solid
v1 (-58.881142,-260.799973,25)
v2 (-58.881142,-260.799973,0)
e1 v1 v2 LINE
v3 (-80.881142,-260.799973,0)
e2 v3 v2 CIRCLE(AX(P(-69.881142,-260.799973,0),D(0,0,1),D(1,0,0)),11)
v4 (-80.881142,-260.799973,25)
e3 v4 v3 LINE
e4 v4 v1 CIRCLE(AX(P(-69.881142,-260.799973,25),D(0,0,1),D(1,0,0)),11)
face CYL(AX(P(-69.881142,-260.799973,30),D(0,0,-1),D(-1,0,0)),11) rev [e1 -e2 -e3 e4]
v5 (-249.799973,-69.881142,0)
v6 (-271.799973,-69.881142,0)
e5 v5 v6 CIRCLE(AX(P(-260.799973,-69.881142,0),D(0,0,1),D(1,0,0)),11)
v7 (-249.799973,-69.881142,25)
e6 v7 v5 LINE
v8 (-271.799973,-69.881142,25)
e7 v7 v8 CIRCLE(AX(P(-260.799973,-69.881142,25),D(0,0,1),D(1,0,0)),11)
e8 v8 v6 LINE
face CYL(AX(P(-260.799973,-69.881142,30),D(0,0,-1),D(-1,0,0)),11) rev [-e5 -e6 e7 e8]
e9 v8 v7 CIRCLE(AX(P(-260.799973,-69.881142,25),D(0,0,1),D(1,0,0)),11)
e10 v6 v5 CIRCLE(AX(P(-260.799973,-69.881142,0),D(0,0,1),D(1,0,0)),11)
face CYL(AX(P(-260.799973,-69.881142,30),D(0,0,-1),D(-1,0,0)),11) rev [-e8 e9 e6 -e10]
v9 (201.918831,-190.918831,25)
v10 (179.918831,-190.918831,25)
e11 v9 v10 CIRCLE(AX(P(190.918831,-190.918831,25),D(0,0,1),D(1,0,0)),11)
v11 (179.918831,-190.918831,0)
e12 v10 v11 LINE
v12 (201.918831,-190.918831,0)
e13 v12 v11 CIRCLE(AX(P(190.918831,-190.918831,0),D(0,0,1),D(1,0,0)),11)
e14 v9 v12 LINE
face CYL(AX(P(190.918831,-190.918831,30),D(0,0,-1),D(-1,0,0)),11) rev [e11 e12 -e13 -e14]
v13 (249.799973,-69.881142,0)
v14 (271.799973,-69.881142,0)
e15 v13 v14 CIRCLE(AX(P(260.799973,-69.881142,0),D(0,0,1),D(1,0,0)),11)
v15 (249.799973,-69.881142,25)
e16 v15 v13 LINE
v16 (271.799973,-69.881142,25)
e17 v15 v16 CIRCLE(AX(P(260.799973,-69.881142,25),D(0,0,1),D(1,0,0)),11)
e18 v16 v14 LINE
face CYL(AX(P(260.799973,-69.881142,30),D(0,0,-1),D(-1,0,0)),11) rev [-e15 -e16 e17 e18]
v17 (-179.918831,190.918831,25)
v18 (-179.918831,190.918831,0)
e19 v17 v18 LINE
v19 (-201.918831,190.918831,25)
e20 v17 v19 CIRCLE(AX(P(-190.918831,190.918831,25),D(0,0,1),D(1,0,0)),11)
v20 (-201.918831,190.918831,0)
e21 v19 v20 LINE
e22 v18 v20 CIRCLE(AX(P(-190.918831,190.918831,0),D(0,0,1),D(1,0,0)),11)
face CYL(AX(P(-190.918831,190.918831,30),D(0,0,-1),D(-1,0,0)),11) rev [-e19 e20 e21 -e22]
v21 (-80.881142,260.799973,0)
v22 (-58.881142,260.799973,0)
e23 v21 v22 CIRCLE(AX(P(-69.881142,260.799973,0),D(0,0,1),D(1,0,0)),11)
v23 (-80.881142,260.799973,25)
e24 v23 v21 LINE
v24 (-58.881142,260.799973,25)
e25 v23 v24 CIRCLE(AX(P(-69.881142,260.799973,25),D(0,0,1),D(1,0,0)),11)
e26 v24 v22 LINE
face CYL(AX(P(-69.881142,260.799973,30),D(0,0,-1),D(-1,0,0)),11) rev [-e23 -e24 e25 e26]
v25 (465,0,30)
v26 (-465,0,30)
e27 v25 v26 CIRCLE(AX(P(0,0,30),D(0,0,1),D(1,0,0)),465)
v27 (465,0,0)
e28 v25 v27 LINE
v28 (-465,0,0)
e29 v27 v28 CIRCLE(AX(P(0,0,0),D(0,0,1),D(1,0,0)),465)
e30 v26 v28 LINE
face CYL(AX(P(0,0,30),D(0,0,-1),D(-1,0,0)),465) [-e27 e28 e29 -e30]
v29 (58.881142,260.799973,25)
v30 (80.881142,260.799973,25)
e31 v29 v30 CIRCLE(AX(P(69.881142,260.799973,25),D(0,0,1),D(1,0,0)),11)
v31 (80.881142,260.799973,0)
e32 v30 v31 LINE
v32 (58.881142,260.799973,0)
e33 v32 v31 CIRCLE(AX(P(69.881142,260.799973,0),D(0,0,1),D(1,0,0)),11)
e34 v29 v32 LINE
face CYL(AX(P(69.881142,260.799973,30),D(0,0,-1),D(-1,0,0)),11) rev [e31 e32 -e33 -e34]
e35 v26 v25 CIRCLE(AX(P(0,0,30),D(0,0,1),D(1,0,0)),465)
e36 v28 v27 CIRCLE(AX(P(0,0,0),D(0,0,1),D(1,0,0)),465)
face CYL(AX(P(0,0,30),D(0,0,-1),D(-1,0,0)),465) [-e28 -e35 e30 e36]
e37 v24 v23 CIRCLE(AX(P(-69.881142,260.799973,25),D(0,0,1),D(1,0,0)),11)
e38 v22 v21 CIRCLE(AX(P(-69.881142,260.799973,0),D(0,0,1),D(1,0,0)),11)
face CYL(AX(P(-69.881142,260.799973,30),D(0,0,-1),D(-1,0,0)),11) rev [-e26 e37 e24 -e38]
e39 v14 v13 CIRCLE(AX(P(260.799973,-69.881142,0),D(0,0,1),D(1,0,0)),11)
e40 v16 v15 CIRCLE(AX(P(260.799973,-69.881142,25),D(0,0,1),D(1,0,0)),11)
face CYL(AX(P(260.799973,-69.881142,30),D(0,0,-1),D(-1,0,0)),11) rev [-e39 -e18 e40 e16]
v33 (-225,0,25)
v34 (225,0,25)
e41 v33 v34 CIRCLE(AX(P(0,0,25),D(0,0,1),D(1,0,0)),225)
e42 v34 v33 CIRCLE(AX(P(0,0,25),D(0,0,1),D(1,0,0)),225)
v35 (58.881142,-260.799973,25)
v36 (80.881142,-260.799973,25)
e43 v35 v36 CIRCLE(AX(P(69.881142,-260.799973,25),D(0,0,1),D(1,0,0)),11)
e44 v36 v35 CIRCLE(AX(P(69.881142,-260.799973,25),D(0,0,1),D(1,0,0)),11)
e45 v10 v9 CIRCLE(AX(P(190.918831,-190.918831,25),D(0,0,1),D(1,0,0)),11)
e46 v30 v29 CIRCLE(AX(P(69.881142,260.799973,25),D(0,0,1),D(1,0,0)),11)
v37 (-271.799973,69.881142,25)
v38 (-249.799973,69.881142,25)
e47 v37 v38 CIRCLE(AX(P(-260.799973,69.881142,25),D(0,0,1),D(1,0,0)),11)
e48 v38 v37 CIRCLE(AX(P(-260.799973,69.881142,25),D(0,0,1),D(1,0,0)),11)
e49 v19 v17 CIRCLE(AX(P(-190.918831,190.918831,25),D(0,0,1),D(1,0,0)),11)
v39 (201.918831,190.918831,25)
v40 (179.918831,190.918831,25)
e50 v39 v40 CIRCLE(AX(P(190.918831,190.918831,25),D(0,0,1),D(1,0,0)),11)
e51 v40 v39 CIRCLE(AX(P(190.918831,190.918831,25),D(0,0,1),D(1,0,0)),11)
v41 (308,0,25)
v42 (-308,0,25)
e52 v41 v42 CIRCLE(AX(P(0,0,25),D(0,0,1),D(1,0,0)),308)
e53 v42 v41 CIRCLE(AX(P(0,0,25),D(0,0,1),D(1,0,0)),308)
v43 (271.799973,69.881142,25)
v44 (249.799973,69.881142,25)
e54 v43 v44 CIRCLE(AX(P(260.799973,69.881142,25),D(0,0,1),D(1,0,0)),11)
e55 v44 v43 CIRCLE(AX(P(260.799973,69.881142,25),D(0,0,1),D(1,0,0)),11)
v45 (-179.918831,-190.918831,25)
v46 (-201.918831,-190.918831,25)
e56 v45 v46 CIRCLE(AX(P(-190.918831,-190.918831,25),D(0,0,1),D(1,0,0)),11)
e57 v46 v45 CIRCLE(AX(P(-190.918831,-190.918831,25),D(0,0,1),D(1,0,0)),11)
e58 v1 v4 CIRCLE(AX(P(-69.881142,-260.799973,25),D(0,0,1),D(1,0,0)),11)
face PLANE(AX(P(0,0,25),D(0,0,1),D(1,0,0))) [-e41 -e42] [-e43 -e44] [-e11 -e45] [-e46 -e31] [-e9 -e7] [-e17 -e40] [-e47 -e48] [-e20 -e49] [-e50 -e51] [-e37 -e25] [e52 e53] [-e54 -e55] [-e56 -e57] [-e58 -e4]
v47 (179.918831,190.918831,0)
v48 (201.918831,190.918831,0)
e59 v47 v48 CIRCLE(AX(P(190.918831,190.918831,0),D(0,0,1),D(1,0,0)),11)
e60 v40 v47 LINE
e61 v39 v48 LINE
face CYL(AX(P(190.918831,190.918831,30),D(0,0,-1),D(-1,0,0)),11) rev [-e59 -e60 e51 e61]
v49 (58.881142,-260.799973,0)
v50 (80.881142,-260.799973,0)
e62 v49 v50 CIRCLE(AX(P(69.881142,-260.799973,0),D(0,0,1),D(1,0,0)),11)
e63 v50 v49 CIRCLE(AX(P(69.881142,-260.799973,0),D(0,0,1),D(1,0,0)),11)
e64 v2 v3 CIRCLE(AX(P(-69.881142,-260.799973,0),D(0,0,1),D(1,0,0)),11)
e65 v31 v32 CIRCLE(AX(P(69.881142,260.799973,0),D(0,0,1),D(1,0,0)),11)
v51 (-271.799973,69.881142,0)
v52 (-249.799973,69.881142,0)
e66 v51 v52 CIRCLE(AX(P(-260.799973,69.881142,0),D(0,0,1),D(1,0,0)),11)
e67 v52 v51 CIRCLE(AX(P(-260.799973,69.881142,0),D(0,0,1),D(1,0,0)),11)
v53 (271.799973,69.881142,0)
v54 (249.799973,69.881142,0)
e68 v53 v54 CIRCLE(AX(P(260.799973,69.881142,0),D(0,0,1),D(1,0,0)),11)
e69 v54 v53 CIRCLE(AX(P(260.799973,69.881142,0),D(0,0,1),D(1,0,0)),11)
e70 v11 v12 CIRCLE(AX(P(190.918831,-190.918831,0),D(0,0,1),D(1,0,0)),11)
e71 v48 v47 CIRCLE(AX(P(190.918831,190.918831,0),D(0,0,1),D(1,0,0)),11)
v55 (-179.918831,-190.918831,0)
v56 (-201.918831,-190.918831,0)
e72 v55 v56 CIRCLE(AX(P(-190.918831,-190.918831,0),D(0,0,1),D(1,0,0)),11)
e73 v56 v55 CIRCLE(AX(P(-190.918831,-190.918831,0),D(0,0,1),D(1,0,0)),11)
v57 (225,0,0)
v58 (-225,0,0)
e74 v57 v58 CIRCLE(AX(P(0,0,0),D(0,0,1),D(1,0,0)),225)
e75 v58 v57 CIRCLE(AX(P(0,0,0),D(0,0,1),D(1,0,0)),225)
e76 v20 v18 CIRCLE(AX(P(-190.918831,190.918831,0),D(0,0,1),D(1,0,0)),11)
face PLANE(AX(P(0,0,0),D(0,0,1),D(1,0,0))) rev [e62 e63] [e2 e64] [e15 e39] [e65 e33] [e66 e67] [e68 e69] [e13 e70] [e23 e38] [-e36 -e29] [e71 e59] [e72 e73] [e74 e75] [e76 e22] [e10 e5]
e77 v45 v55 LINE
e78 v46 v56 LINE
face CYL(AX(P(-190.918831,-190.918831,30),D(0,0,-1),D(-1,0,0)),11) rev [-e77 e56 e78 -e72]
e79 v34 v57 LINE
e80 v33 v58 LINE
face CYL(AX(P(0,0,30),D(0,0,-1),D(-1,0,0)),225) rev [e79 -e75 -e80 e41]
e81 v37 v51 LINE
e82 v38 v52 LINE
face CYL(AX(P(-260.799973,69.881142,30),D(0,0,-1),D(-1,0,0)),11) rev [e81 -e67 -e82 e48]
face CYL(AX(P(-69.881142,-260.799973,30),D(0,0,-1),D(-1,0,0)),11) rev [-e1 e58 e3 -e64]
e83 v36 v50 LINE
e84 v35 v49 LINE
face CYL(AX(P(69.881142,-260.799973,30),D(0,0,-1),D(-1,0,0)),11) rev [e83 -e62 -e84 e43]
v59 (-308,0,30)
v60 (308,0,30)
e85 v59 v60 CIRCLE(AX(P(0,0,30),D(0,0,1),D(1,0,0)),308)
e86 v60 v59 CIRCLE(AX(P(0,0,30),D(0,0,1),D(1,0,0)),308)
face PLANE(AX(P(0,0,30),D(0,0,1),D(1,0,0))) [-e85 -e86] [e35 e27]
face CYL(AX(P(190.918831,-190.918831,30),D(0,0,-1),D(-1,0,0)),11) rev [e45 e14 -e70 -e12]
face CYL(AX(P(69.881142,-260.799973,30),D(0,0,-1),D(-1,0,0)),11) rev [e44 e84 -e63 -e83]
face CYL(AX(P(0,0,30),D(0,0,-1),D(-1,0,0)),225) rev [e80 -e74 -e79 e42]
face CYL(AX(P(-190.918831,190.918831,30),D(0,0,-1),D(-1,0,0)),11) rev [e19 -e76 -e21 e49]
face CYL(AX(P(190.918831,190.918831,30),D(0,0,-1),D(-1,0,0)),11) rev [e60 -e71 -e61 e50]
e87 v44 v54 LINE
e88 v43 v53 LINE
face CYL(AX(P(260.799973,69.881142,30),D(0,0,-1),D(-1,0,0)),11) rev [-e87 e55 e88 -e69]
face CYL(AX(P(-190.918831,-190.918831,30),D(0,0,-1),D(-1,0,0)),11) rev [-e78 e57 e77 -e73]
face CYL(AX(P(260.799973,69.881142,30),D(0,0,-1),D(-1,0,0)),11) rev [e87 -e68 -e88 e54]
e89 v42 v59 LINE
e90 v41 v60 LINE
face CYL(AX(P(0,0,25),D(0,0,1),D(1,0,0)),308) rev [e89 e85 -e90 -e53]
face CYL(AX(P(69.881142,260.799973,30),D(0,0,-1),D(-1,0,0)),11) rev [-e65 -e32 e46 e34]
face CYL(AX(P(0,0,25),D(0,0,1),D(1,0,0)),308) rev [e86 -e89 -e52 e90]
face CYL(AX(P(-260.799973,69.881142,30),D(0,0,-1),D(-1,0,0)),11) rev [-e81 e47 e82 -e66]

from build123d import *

# Parameters (mm, degrees)
SKETCH1_R               = 465
SKETCH1_R_2             = 225
BOSS_EXTRUDE1_DEPTH     = 30
SKETCH2_R               = 308
CUT_EXTRUDE1_DEPTH      = 5
CUT_EXTRUDE7_DEPTH      = 659.293247725
CUT_EXTRUDE7_DEPTH_BACK = 659.293247725
SKETCH4_R               = 11


with BuildPart() as part:
    # Sketch1 → Boss-Extrude1 (new body)
    with BuildSketch(Plane.XY):
        Circle(SKETCH1_R)
        Circle(SKETCH1_R_2, mode=Mode.SUBTRACT)
    extrude(amount=BOSS_EXTRUDE1_DEPTH)

    # Sketch2 → Cut-Extrude1 (cut)
    with BuildSketch(Plane.XY.offset(30)):
        Circle(SKETCH2_R)
    extrude(amount=-CUT_EXTRUDE1_DEPTH, mode=Mode.SUBTRACT)

    # Sketch4 → Cut-Extrude7 (cut, two sides: drawn at the far end of the back side and taken through both)
    with BuildSketch(Plane(origin=(0, 0, 0), x_dir=(-1, 0, 0), z_dir=(0, 0, -1)).offset(-CUT_EXTRUDE7_DEPTH_BACK)):
        with Locations(Location((-260.799973098, 69.881142178, 0), (0, 0, 180))):
            Circle(SKETCH4_R)
        with Locations(Location((-190.91883092, 190.91883092, 0), (0, 0, 180))):
            Circle(SKETCH4_R)
        with Locations(Location((-69.881142178, 260.799973098, 0), (0, 0, 180))):
            Circle(SKETCH4_R)
        with Locations(Location((69.881142178, 260.799973098, 0), (0, 0, 180))):
            Circle(SKETCH4_R)
        with Locations(Location((190.91883092, 190.91883092, 0), (0, 0, 180))):
            Circle(SKETCH4_R)
        with Locations(Location((260.799973098, 69.881142178, 0), (0, 0, 180))):
            Circle(SKETCH4_R)
        with Locations(Location((260.799973098, -69.881142178, 0), (0, 0, 180))):
            Circle(SKETCH4_R)
        with Locations(Location((190.91883092, -190.91883092, 0), (0, 0, 180))):
            Circle(SKETCH4_R)
        with Locations(Location((69.881142178, -260.799973098, 0), (0, 0, 180))):
            Circle(SKETCH4_R)
        with Locations(Location((-69.881142178, -260.799973098, 0), (0, 0, 180))):
            Circle(SKETCH4_R)
        with Locations(Location((-190.91883092, -190.91883092, 0), (0, 0, 180))):
            Circle(SKETCH4_R)
        with Locations(Location((-260.799973098, -69.881142178, 0), (0, 0, 180))):
            Circle(SKETCH4_R)
    extrude(amount=CUT_EXTRUDE7_DEPTH + CUT_EXTRUDE7_DEPTH_BACK, mode=Mode.SUBTRACT)


solid = part.part
